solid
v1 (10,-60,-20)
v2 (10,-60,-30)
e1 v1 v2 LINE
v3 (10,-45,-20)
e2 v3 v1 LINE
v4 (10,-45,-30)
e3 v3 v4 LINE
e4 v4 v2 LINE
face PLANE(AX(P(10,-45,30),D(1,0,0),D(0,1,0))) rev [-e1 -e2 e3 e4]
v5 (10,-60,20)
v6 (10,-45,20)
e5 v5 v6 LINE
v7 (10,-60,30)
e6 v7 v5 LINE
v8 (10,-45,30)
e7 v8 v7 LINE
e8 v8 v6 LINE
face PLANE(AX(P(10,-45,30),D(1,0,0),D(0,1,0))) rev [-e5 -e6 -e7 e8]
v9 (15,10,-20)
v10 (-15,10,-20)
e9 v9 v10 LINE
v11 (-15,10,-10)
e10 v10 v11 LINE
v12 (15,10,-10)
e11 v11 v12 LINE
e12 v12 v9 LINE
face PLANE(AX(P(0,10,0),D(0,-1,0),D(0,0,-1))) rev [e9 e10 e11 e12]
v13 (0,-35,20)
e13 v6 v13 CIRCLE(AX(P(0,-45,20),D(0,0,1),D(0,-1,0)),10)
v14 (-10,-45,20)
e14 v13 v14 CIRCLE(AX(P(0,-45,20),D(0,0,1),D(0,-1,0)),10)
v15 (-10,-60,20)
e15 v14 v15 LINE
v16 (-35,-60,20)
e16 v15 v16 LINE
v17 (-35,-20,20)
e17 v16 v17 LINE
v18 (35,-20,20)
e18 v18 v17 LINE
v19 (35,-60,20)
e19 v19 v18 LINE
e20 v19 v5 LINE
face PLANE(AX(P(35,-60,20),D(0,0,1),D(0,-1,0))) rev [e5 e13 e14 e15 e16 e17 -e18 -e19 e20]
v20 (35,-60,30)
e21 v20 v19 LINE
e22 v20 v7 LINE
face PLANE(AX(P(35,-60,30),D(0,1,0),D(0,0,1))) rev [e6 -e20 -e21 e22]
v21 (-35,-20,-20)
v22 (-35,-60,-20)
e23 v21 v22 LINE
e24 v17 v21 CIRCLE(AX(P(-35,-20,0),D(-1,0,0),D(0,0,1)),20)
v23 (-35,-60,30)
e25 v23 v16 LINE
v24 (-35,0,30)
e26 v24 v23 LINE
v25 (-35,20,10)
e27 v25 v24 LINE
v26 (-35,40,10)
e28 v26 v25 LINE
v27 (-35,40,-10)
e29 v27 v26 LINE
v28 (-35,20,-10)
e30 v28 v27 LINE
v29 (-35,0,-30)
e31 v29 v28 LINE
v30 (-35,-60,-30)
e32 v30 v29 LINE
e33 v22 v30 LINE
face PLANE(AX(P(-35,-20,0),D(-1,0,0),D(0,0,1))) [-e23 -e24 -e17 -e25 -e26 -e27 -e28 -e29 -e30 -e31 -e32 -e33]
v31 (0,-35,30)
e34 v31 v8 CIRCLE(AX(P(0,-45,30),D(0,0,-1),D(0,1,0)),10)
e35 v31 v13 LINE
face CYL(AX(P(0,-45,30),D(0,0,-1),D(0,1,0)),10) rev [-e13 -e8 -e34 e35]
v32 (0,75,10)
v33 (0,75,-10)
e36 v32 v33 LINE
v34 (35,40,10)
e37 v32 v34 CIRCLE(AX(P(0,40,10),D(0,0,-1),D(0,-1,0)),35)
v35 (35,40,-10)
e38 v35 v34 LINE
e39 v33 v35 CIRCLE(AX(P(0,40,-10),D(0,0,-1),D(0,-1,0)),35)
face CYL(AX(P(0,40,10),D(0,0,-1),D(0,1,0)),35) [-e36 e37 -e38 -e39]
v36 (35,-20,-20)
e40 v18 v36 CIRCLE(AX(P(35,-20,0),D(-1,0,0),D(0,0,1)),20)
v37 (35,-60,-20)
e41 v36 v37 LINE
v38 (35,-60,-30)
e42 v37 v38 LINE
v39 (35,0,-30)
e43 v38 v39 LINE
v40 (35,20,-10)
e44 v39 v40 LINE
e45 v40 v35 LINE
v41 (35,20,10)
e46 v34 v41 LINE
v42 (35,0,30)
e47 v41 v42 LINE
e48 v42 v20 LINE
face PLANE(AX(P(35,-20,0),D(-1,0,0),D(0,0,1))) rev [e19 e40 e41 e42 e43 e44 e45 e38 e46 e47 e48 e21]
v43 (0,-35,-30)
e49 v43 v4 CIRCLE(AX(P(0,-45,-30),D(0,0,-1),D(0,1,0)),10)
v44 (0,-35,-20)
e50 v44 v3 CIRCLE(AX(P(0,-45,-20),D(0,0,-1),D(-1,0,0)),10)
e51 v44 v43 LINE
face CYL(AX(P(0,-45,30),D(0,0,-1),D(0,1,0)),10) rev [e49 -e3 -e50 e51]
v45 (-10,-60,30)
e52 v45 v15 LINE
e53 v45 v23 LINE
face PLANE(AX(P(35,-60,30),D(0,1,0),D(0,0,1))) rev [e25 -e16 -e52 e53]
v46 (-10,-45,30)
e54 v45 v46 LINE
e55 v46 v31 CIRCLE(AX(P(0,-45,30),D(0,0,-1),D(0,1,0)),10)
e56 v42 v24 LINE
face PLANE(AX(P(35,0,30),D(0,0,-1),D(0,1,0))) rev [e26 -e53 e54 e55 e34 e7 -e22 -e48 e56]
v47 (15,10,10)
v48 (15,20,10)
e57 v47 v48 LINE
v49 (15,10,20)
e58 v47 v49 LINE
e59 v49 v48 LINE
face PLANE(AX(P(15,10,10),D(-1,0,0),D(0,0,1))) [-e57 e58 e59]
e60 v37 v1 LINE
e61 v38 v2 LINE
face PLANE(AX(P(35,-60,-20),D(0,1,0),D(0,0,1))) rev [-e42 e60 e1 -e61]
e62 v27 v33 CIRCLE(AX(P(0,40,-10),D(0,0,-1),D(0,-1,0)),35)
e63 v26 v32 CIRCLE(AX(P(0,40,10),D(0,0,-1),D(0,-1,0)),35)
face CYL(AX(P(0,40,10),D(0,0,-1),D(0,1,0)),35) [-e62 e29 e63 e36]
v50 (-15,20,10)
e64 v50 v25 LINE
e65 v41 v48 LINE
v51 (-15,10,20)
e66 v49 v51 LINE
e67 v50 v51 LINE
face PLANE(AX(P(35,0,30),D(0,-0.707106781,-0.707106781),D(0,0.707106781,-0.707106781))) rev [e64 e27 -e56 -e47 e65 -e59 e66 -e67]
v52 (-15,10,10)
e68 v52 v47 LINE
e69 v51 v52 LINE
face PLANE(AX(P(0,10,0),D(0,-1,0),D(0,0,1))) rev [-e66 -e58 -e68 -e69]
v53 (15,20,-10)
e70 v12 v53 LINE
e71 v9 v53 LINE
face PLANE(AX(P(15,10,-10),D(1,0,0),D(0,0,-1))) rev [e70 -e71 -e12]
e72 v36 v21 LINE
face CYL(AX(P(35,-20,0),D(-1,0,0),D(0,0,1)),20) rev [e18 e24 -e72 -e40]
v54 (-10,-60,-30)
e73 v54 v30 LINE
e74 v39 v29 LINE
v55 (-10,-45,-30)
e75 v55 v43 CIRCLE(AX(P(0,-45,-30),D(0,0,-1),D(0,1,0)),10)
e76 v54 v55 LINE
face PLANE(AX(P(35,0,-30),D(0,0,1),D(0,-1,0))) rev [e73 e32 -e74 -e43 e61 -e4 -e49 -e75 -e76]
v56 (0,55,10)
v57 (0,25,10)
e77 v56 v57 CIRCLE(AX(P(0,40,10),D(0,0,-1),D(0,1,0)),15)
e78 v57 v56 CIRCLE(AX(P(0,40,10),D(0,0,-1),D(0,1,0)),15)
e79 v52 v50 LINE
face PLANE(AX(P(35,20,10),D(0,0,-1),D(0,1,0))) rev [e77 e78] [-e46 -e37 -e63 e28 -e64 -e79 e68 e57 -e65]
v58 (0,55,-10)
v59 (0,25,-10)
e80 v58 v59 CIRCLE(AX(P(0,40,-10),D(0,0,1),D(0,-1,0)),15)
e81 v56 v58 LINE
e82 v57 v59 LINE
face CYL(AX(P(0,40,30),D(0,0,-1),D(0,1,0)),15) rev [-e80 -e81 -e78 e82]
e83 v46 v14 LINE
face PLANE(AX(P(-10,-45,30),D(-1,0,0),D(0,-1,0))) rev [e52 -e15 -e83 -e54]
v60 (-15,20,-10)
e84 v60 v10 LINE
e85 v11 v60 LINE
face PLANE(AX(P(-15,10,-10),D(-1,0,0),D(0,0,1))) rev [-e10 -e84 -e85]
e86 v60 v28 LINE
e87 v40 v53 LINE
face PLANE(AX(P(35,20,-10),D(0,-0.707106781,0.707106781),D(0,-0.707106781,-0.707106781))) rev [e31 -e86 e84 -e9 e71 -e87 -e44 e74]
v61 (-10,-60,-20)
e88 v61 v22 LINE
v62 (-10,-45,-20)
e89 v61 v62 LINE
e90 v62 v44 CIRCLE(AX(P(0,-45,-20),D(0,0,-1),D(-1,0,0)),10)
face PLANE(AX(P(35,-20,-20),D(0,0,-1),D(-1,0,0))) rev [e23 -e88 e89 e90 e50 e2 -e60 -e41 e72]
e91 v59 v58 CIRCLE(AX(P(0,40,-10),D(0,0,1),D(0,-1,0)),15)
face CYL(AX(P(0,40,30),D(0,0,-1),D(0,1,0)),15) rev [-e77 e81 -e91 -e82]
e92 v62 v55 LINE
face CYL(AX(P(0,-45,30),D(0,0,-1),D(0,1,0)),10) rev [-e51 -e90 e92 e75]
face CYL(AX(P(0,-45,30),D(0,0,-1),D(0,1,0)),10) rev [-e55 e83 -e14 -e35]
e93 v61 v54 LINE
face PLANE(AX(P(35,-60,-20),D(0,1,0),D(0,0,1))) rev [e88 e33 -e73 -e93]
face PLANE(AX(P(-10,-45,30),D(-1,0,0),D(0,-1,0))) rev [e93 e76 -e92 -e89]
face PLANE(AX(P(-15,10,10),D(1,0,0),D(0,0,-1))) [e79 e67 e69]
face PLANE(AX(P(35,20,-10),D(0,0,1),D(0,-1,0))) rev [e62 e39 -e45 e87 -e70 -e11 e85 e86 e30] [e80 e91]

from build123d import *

# Parameters (mm, degrees)
ARCHED_BASE_BLOCK_DEPTH = 35
HINGE_EAR_DEPTH         = 20
HINGE_BORE_DEPTH        = 92.923881554
HINGE_BORE_DEPTH_BACK   = 92.923881554
HINGE_BORE_SKETCH_R     = 15
EAR_START               = 20
EAR_ROOT_NOTCH_SKETCH_W = 30
EAR_ROOT_NOTCH_SKETCH_H = 10
EAR_ROOT_NOTCH_DEPTH    = 10


with BuildPart() as part:
    # Arched Base Profile Sketch → Arched Base Block (new, symmetric)
    with BuildSketch(Plane(origin=(0, 0, 0), x_dir=(0, 0, -1), z_dir=(1, 0, 0))):
        with BuildLine():
            Line((-30, 0), (-10, 20))
            Line((-10, 20), (-10, 40))
            Line((-10, 40), (10, 40))
            Line((10, 40), (10, 20))
            Line((10, 20), (30, 0))
            Line((30, 0), (30, -60))
            Line((30, -60), (20, -60))
            Line((20, -60), (20, -20))
            ThreePointArc((20, -20), (0, 0), (-20, -20))
            Line((-20, -20), (-20, -60))
            Line((-20, -60), (-30, -60))
            Line((-30, -60), (-30, 0))
        make_face()
    extrude(amount=ARCHED_BASE_BLOCK_DEPTH, both=True)

    # Hinge Ear Sketch → Hinge Ear (add)
    with BuildSketch(Plane(origin=(0, 0, -10), x_dir=(-1, 0, 0), z_dir=(0, 0, -1))):
        with BuildLine():
            Line((-35, 40), (35, 40))
            ThreePointArc((35, 40), (0, 75), (-35, 40))
        make_face()
    extrude(amount=-HINGE_EAR_DEPTH)

    # Hinge Bore Sketch → Hinge Bore (cut, two sides: drawn at the far end of the back side and taken through both)
    with BuildSketch(Plane(origin=(0, 0, -10), x_dir=(-1, 0, 0), z_dir=(0, 0, -1)).offset(-HINGE_BORE_DEPTH_BACK)):
        with Locations(Location((0, 40, 0), (0, 0, 90))):
            Circle(HINGE_BORE_SKETCH_R)
        with BuildLine():
            Line((-10, -45), (-10, -60))
            Line((-10, -60), (10, -60))
            Line((10, -60), (10, -45))
            ThreePointArc((10, -45), (0, -35), (-10, -45))
        make_face()
    extrude(amount=HINGE_BORE_DEPTH + HINGE_BORE_DEPTH_BACK, mode=Mode.SUBTRACT)

    # Ear Root Notch Sketch → Ear Root Notch (cut)
    with BuildSketch(Plane(origin=(0, 0, 0), x_dir=(1, 0, 0), z_dir=(0, 1, 0)).offset(EAR_START)):
        with Locations((0, 15)):
            Rectangle(EAR_ROOT_NOTCH_SKETCH_W, EAR_ROOT_NOTCH_SKETCH_H)
    ear_root_notch = extrude(amount=-EAR_ROOT_NOTCH_DEPTH, mode=Mode.SUBTRACT)

    # Ear Root Notch Mirror: Ear Root Notch across plane
    add(ear_root_notch.mirror(Plane.XY), mode=Mode.SUBTRACT)


solid = part.part
